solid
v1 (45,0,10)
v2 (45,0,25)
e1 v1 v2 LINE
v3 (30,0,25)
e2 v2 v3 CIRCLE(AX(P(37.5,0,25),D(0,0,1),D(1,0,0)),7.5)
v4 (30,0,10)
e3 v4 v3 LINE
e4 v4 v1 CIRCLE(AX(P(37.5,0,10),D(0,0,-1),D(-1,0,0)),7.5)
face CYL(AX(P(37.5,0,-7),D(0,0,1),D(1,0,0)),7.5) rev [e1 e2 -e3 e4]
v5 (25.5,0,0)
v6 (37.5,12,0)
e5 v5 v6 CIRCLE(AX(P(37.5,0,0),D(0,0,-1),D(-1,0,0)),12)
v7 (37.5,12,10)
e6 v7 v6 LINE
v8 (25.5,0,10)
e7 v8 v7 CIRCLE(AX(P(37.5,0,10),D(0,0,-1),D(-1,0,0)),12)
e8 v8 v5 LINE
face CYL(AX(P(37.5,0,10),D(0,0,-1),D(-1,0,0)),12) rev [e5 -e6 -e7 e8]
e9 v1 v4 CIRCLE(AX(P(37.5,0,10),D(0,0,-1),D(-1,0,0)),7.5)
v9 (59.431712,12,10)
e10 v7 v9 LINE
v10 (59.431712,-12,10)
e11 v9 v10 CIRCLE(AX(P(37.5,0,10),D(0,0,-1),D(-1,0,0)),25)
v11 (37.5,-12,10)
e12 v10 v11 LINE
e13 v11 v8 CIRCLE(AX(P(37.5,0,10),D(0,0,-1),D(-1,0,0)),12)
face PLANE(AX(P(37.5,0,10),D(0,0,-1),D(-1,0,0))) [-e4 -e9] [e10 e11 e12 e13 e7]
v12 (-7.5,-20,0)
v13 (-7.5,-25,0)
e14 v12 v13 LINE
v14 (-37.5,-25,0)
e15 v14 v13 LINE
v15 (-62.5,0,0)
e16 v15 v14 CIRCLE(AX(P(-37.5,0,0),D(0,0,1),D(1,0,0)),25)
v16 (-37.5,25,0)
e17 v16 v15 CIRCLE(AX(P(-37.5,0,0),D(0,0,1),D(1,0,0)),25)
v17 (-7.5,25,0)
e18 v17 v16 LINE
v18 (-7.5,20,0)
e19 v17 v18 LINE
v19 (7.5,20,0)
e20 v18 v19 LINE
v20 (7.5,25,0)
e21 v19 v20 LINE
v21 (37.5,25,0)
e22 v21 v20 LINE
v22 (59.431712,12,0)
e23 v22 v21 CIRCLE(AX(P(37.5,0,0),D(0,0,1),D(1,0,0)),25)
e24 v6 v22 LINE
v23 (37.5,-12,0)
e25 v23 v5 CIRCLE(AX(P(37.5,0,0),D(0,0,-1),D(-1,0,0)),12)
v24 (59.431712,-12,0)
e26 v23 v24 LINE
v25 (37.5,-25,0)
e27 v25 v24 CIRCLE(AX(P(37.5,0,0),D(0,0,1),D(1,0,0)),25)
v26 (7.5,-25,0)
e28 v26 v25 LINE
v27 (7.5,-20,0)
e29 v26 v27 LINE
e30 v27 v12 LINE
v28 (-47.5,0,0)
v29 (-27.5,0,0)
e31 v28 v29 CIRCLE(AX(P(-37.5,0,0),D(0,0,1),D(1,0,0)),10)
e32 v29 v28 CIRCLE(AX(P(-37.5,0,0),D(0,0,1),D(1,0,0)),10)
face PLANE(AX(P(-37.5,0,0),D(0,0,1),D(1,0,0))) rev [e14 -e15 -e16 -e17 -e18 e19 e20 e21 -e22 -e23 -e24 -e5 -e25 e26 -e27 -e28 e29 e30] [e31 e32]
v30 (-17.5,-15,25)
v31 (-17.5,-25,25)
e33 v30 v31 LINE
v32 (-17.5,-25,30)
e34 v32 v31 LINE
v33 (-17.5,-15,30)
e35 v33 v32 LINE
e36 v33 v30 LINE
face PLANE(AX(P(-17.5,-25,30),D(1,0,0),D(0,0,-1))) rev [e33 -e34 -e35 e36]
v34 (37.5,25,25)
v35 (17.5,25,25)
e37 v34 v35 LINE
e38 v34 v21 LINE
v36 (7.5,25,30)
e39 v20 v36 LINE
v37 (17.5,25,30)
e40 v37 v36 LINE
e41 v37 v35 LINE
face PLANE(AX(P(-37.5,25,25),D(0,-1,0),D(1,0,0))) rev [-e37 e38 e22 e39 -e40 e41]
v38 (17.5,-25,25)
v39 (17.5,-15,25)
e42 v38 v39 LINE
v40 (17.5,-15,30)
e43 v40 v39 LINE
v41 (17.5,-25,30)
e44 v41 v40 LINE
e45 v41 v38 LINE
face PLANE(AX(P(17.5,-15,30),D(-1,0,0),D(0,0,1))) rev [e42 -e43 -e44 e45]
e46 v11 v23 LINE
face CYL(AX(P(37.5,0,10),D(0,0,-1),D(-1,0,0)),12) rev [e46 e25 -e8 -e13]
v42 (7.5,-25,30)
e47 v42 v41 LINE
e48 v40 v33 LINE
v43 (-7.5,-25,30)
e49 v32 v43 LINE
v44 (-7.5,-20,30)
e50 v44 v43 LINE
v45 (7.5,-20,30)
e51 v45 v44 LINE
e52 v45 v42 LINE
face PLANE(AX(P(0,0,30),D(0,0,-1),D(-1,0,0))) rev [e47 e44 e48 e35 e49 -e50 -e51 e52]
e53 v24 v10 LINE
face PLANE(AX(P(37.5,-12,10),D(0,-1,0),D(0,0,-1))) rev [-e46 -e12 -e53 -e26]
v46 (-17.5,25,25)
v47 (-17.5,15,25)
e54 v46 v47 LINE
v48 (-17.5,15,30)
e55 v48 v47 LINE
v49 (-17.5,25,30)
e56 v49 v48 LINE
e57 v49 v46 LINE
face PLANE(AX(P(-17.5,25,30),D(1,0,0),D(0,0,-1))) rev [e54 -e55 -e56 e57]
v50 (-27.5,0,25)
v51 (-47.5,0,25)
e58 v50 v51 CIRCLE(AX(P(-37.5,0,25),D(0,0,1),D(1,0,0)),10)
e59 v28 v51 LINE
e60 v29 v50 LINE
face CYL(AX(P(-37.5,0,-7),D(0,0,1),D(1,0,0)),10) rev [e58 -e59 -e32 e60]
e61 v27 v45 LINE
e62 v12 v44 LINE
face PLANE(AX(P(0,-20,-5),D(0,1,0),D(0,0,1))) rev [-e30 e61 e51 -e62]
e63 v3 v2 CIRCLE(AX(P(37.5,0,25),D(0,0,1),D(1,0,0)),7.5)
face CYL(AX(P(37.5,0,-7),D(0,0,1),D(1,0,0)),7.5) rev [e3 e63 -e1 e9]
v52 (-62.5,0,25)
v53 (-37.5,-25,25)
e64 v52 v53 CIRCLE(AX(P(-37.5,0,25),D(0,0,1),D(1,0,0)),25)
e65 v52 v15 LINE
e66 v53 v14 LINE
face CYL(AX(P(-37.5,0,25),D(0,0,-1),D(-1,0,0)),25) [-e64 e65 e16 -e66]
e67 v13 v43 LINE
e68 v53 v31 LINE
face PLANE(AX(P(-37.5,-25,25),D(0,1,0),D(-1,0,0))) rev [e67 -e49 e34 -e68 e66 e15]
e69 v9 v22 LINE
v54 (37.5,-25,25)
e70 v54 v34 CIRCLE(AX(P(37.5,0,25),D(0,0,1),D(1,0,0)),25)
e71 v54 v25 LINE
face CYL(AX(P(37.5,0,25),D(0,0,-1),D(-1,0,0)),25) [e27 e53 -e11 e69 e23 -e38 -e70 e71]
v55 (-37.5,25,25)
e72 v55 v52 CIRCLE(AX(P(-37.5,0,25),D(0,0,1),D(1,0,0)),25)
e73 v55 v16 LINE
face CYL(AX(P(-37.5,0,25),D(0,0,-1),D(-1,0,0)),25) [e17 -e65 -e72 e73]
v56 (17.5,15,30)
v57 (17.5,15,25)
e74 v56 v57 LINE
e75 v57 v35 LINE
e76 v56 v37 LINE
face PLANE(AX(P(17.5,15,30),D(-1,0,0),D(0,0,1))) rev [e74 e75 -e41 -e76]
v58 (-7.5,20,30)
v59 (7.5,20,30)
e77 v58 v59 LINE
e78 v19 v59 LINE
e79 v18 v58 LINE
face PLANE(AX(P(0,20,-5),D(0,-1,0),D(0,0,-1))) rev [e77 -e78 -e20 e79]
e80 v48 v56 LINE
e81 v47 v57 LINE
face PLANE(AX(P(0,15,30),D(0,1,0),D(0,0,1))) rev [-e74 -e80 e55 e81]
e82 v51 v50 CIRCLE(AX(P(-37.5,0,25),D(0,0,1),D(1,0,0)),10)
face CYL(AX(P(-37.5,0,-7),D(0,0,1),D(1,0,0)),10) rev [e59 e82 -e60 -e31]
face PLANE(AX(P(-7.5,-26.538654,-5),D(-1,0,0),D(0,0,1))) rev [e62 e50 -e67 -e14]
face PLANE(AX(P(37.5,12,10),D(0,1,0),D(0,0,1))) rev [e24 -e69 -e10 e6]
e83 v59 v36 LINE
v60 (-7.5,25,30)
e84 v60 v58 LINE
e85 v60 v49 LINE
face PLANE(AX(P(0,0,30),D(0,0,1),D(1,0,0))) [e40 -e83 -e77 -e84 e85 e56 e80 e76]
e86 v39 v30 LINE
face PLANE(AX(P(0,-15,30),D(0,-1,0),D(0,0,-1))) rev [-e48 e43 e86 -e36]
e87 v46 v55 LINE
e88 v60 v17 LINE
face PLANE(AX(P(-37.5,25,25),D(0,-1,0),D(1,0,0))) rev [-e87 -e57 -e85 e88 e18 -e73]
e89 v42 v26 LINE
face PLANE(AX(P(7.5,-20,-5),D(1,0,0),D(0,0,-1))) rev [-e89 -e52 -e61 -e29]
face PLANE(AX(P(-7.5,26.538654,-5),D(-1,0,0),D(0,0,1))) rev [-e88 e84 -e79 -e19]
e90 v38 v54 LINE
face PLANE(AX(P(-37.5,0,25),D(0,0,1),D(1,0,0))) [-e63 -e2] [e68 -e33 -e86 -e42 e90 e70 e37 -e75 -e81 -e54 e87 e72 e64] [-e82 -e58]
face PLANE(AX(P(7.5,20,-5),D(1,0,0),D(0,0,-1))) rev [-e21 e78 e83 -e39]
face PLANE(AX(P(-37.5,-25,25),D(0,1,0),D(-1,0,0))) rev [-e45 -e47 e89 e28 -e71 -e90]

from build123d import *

# Parameters (mm, degrees)
LINK_BODY_DEPTH       = 25
SIDE_PADS_35X10_DEPTH = 5
T_SLOTS_DEPTH         = 35
CROSS_SLOT_12MM_DEPTH = 10
EYE_BORE_20_SKETCH_R  = 10
EYE_BORE_20_DEPTH     = 32
EYE_BORE_15_SKETCH_R  = 7.5
EYE_BORE_15_DEPTH     = 32


with BuildPart() as part:
    # Link Profile Sketch → Link Body (new body)
    with BuildSketch(Plane.XY):
        with BuildLine():
            Line((-37.5, 25), (37.5, 25))
            ThreePointArc((37.5, 25), (62.5, 0), (37.5, -25))
            Line((37.5, -25), (-37.5, -25))
            ThreePointArc((-37.5, -25), (-62.5, 0), (-37.5, 25))
        make_face()
    extrude(amount=LINK_BODY_DEPTH)

    # Side Pads Sketch → Side Pads 35x10 (add)
    with BuildSketch(Plane.XY.offset(25)):
        Polygon((0, -15), (17.5, -15), (17.5, -25), (-17.5, -25), (-17.5, -15), align=None)
        Polygon((-17.5, 15), (0, 15), (17.5, 15), (17.5, 25), (-17.5, 25), align=None)
    extrude(amount=SIDE_PADS_35X10_DEPTH)

    # T-Slots Sketch → T-Slots (cut)
    with BuildSketch(Plane.XY.offset(30)):
        Polygon((0, -20), (7.5, -20), (7.5, -26.538654193), (-7.5, -26.538654193), (-7.5, -20), align=None)
        Polygon((-7.5, 20), (0, 20), (7.5, 20), (7.5, 26.538654193), (-7.5, 26.538654193), align=None)
    extrude(amount=-T_SLOTS_DEPTH, mode=Mode.SUBTRACT)

    # Cross Slot Sketch → Cross Slot 12mm (cut)
    with BuildSketch(Plane(origin=(0, 0, 0), x_dir=(-1, 0, 0), z_dir=(0, 0, -1))):
        with BuildLine():
            Line((-37.5, 12), (-67.446025863, 12))
            Line((-67.446025863, 12), (-67.446025863, -12))
            Line((-67.446025863, -12), (-37.5, -12))
            ThreePointArc((-37.5, -12), (-25.5, 0), (-37.5, 12))
        make_face()
    extrude(amount=-CROSS_SLOT_12MM_DEPTH, mode=Mode.SUBTRACT)

    # Eye Bore Ø20 Sketch → Eye Bore Ø20 (cut)
    with BuildSketch(Plane.XY.offset(25)):
        with Locations((-37.5, 0)):
            Circle(EYE_BORE_20_SKETCH_R)
    extrude(amount=-EYE_BORE_20_DEPTH, mode=Mode.SUBTRACT)

    # Eye Bore Ø15 Sketch → Eye Bore Ø15 (cut)
    with BuildSketch(Plane.XY.offset(25)):
        with Locations((37.5, 0)):
            Circle(EYE_BORE_15_SKETCH_R)
    extrude(amount=-EYE_BORE_15_DEPTH, mode=Mode.SUBTRACT)


solid = part.part
